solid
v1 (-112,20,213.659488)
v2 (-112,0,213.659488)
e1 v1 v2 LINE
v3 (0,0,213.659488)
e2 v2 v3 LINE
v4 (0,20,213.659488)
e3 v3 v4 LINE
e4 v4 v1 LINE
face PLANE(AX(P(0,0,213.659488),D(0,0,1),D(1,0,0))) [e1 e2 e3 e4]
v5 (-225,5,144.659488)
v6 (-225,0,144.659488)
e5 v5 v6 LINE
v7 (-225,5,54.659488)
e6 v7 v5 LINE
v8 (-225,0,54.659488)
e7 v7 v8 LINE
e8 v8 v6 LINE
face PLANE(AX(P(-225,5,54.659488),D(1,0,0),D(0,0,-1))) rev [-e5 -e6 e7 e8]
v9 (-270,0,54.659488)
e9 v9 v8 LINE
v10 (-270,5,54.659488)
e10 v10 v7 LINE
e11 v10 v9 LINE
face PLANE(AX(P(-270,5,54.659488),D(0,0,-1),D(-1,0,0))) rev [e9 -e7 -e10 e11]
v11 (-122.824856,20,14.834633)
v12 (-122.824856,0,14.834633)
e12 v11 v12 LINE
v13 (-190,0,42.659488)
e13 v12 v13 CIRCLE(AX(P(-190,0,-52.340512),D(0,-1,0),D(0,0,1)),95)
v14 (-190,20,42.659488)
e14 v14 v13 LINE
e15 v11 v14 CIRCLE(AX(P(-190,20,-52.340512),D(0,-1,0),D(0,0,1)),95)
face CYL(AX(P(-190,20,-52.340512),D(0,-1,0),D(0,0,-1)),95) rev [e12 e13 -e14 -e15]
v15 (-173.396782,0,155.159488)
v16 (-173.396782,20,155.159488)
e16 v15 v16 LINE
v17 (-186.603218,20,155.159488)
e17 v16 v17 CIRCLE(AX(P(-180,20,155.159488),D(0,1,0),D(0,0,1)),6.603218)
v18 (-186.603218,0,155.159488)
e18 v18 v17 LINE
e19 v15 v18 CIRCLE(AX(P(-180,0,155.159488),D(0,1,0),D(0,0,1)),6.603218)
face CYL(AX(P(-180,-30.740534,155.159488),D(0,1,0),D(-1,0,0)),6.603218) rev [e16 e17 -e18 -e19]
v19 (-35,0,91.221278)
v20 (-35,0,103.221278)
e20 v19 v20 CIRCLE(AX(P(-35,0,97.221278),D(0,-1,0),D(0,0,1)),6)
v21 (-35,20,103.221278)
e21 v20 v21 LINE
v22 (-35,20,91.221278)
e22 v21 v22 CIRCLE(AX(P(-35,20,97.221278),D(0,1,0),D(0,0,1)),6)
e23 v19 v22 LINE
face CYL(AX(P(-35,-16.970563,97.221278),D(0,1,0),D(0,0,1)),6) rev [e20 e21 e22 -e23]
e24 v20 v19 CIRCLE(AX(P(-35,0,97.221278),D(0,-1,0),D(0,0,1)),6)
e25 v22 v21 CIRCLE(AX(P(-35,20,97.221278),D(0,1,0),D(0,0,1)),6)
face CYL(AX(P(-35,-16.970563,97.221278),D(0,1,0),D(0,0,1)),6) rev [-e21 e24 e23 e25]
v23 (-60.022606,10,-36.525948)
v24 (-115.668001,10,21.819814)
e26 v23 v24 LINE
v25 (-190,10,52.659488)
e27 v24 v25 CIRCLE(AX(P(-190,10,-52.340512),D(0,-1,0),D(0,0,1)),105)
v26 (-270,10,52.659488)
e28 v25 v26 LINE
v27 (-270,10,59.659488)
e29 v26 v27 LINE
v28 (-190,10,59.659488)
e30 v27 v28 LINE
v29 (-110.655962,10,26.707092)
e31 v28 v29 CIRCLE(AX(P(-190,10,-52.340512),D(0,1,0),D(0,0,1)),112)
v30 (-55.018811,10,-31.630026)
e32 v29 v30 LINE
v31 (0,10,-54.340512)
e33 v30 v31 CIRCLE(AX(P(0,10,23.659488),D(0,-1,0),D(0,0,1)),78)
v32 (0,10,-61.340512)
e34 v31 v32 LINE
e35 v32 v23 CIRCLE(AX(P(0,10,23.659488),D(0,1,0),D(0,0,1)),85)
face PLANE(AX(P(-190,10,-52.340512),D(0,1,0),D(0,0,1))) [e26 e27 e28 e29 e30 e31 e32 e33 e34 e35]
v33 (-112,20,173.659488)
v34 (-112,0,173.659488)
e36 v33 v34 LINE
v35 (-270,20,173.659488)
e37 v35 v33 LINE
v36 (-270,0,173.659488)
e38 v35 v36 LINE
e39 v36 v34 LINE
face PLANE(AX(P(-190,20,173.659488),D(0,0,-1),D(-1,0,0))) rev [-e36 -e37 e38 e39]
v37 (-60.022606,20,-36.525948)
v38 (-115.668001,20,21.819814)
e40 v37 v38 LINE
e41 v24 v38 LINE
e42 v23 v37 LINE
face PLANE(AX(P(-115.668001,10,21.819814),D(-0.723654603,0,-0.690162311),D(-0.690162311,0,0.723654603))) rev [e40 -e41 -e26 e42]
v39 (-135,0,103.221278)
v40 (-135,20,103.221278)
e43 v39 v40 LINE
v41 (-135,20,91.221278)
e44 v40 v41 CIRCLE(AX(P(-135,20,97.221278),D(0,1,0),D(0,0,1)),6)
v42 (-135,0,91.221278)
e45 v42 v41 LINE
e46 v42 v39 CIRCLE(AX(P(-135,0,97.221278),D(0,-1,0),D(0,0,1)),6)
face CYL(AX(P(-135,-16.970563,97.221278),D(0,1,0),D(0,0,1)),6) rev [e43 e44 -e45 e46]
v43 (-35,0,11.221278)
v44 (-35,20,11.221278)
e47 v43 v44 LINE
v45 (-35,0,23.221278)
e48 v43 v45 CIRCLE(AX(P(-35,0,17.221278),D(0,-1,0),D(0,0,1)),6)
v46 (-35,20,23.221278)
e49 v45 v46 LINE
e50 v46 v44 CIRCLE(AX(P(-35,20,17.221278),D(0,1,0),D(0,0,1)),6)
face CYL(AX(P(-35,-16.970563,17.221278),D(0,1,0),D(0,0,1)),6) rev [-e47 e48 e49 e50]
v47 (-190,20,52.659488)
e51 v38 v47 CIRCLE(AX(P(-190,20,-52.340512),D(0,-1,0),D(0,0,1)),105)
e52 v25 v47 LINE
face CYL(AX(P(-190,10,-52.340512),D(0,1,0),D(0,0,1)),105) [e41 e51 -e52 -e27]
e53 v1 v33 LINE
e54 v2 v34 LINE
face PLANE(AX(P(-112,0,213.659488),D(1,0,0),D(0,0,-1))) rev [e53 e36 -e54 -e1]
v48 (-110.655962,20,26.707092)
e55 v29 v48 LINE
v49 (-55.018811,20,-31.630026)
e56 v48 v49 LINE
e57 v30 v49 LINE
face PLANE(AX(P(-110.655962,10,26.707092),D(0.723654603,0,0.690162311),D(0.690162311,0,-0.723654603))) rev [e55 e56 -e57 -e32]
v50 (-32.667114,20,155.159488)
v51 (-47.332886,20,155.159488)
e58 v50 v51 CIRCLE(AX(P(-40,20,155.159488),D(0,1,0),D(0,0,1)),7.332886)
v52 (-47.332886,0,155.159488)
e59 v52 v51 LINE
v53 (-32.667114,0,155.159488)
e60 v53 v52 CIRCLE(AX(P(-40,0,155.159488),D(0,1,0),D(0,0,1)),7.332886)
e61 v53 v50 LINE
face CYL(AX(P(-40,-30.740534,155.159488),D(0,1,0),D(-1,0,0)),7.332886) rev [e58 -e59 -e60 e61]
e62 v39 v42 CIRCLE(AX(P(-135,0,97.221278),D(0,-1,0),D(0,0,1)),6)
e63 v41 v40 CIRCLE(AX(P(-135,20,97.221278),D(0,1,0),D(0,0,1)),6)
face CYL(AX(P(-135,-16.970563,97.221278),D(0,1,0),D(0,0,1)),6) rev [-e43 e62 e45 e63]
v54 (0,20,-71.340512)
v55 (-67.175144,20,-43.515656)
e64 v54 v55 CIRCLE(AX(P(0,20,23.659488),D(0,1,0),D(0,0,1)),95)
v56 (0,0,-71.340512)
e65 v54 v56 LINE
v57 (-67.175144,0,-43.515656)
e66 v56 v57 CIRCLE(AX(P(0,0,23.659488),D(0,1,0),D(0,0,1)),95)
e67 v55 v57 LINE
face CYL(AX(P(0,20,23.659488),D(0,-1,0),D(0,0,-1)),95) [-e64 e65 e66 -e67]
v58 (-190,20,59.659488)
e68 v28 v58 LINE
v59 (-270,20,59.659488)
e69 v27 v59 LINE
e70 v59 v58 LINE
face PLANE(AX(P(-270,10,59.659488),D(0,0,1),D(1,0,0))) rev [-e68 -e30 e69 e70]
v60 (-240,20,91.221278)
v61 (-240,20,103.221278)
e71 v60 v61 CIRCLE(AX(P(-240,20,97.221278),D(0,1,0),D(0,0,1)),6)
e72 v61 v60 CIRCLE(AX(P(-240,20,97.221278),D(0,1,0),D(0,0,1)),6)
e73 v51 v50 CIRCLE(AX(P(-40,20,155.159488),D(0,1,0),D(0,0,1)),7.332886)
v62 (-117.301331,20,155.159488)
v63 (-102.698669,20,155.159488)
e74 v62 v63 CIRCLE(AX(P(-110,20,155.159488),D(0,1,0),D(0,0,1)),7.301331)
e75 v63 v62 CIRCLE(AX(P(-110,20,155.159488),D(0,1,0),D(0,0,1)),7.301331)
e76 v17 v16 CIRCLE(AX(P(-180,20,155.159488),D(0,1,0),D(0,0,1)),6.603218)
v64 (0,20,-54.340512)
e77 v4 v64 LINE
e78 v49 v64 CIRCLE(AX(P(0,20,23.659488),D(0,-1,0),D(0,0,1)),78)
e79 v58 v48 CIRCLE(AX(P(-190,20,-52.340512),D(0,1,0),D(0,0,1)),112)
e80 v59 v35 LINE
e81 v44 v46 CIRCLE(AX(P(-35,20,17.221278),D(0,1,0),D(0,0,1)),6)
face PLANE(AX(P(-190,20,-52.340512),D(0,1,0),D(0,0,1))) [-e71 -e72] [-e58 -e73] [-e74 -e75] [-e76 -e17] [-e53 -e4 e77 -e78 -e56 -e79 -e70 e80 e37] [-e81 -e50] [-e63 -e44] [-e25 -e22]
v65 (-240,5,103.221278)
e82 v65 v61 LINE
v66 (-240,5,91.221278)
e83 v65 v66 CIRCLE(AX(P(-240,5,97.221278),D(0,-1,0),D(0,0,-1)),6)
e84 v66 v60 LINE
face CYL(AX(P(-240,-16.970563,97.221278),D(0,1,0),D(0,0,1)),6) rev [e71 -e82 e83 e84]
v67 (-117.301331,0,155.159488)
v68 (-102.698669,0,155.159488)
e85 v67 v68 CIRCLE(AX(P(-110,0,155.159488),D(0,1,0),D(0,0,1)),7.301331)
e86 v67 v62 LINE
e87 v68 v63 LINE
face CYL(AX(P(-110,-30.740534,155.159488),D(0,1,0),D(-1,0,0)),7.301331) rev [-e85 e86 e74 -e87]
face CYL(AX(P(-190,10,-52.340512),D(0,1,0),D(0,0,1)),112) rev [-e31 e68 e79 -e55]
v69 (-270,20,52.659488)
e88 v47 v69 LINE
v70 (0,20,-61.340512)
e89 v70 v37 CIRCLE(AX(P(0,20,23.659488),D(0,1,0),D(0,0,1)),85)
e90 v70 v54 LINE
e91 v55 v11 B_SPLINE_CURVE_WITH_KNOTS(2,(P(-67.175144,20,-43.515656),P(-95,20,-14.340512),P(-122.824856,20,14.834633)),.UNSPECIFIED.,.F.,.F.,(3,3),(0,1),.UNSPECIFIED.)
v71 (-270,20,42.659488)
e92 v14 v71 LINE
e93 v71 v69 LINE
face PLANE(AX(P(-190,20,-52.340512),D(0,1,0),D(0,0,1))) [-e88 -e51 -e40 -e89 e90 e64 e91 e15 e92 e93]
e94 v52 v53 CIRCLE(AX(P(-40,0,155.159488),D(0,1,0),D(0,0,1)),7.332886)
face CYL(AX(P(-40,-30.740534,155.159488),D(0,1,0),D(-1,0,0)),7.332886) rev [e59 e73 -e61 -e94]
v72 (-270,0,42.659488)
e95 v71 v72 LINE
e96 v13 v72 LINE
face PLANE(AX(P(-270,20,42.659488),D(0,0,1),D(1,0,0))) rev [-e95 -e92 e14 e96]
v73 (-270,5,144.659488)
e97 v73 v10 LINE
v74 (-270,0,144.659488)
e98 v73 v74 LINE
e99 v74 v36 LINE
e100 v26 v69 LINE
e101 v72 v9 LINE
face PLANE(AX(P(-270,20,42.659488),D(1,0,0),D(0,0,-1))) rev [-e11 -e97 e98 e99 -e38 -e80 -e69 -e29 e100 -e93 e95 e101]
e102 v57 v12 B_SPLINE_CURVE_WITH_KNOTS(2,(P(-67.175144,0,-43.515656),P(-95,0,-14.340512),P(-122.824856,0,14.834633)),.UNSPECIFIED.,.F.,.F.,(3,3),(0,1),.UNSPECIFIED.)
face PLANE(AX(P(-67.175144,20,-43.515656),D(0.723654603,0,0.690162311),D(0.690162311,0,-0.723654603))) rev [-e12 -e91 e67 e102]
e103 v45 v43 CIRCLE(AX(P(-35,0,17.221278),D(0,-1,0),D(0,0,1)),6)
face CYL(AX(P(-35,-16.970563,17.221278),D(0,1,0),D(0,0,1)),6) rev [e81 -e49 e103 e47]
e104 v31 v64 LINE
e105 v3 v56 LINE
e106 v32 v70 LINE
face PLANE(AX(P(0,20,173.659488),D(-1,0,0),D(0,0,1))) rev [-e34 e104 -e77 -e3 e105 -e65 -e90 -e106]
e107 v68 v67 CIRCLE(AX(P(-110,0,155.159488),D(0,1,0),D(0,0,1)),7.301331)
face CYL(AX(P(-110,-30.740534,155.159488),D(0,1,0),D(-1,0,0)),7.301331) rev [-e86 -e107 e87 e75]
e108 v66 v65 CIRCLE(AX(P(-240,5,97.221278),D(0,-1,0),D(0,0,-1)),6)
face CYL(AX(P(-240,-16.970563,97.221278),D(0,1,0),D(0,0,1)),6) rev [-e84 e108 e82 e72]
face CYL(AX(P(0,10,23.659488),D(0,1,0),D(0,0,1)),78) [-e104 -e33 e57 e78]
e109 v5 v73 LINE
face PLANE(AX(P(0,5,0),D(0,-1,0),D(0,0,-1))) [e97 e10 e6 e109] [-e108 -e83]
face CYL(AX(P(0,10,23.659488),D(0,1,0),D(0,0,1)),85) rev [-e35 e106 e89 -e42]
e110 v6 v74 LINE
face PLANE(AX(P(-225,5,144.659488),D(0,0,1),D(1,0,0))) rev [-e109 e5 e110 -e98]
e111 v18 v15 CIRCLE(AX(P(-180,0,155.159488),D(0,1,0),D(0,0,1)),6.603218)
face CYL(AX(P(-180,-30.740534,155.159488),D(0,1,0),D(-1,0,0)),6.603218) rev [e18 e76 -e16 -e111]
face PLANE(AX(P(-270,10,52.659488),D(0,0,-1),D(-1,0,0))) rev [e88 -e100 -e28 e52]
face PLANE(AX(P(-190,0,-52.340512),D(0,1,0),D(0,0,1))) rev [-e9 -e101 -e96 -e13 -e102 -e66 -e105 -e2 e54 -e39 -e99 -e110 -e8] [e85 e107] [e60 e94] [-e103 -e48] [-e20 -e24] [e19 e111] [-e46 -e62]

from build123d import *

# Parameters (mm, degrees)
EXTRUDE_1_DEPTH      = 20
CUT_EXTRUDE_1_DEPTH  = 10
SKETCH_4_W           = 45
SKETCH_4_H           = 90
CUT_EXTRUDE_2_DEPTH  = 5
SKETCH_5_W           = 112
SKETCH_5_H           = 20
EXTRUDE_2_DEPTH      = 40
CUT_EXTRUDE_3_REACH  = 1227.871
SKETCH_6_R           = 6
SKETCH_6_R_2         = 5
CUT_EXTRUDE_4_REACH  = 1228.116
SKETCH_7_R           = 7.332886018
SKETCH_7_R_2         = 7.301331484
SKETCH_7_R_3         = 6.603217824
SKETCH_24_R          = 6
CUT_EXTRUDE_21_DEPTH = 25


with BuildPart() as part:
    # 草图1 → 凸台-拉伸1 (new body)
    with BuildSketch(Plane(origin=(0, 0, 0), x_dir=(1, 0, 0), z_dir=(0, 1, 0))):
        with BuildLine():
            Line((-190, -173.659488393), (0, -173.659488393))
            Line((0, -173.659488393), (0, 71.340511607))
            ThreePointArc((0, 71.340511607), (-36.354926075, 64.109067196), (-67.175144213, 43.51565582))
            add(Edge.make_bspline(
                [(-122.824855787, -14.834632605), (-95, 14.340511607), (-67.175144213, 43.51565582)],
                knots=[0, 0, 0, 1, 1, 1], degree=2))
            ThreePointArc((-122.824855787, -14.834632605), (-153.645073925, -35.428043981), (-190, -42.659488393))
            Line((-190, -42.659488393), (-270, -42.659488393))
            Line((-270, -42.659488393), (-270, -173.659488393))
            Line((-270, -173.659488393), (-190, -173.659488393))
        make_face()
    extrude(amount=EXTRUDE_1_DEPTH)

    # 草图2 → 切除-拉伸1 (cut)
    with BuildSketch(Plane(origin=(0, 20, 0), x_dir=(1, 0, 0), z_dir=(0, 1, 0))):
        with BuildLine():
            Line((-270, -52.659488393), (-190, -52.659488393))
            ThreePointArc((-190, -52.659488393), (-149.762170559, -44.64359576), (-115.668000558, -21.819813762))
            Line((-115.668000558, -21.819813762), (-60.022606457, 36.52594767))
            ThreePointArc((-60.022606457, 36.52594767), (-32.474897495, 54.892284551), (0, 61.340511607))
            Line((0, 61.340511607), (0, 54.340511607))
            ThreePointArc((0, 54.340511607), (-29.760862596, 48.439686759), (-55.01881141, 31.630025903))
            Line((-55.01881141, 31.630025903), (-110.655962205, -26.707092192))
            ThreePointArc((-110.655962205, -26.707092192), (-147.042646878, -51.093843482), (-190, -59.659488393))
            Line((-190, -59.659488393), (-270, -59.659488393))
            Line((-270, -59.659488393), (-270, -52.659488393))
        make_face()
    extrude(amount=-CUT_EXTRUDE_1_DEPTH, mode=Mode.SUBTRACT)

    # 草图4 → 切除-拉伸2 (cut)
    with BuildSketch(Plane.XZ):
        with Locations((-247.5, 99.659488393)):
            Rectangle(SKETCH_4_W, SKETCH_4_H)
    extrude(amount=-CUT_EXTRUDE_2_DEPTH, mode=Mode.SUBTRACT)

    # 草图5 → 凸台-拉伸2 (add)
    with BuildSketch(Plane.XY.offset(173.659488393)):
        with Locations((-56, 10)):
            Rectangle(SKETCH_5_W, SKETCH_5_H)
    extrude(amount=EXTRUDE_2_DEPTH)

    # 切除-拉伸3: up to this face of the body (flat: up to its plane)
    cut_extrude_3_end = Plane(part.part.faces().sort_by_distance((-99.039367246, 0, 91.650022184))[0])
    # 草图6 → 切除-拉伸3 (cut, up to the picked face)
    with BuildSketch(Plane(origin=(600.126281628, 25, -649.482989384), x_dir=(0, 0, -1), z_dir=(0, 1, 0)), mode=Mode.PRIVATE) as cut_extrude_3_sk1:
        with Locations(Location((-666.704267343, 635.126281628, 0), (0, 0, 180))):
            Circle(SKETCH_6_R)
    cut_extrude_3_tool1 = split(extrude(cut_extrude_3_sk1.sketch, amount=-CUT_EXTRUDE_3_REACH, mode=Mode.PRIVATE), bisect_by=cut_extrude_3_end, keep=Keep.BOTH, mode=Mode.PRIVATE)
    # 草图6 → 切除-拉伸3 (cut, up to the picked face)
    with BuildSketch(Plane(origin=(600.126281628, 25, -649.482989384), x_dir=(0, 0, -1), z_dir=(0, 1, 0)), mode=Mode.PRIVATE) as cut_extrude_3_sk2:
        with Locations(Location((-746.704267343, 635.126281628, 0), (0, 0, 180))):
            Circle(SKETCH_6_R_2)
    cut_extrude_3_tool2 = split(extrude(cut_extrude_3_sk2.sketch, amount=-CUT_EXTRUDE_3_REACH, mode=Mode.PRIVATE), bisect_by=cut_extrude_3_end, keep=Keep.BOTH, mode=Mode.PRIVATE)
    # 草图6 → 切除-拉伸3 (cut, up to the picked face)
    with BuildSketch(Plane(origin=(600.126281628, 25, -649.482989384), x_dir=(0, 0, -1), z_dir=(0, 1, 0)), mode=Mode.PRIVATE) as cut_extrude_3_sk3:
        with Locations(Location((-746.704267343, 840.126281628, 0), (0, 0, 180))):
            Circle(SKETCH_6_R)
    cut_extrude_3_tool3 = split(extrude(cut_extrude_3_sk3.sketch, amount=-CUT_EXTRUDE_3_REACH, mode=Mode.PRIVATE), bisect_by=cut_extrude_3_end, keep=Keep.BOTH, mode=Mode.PRIVATE)
    # 草图6 → 切除-拉伸3 (cut, up to the picked face)
    with BuildSketch(Plane(origin=(600.126281628, 25, -649.482989384), x_dir=(0, 0, -1), z_dir=(0, 1, 0)), mode=Mode.PRIVATE) as cut_extrude_3_sk4:
        with Locations(Location((-746.704267343, 735.126281628, 0), (0, 0, 180))):
            Circle(SKETCH_6_R)
    cut_extrude_3_tool4 = split(extrude(cut_extrude_3_sk4.sketch, amount=-CUT_EXTRUDE_3_REACH, mode=Mode.PRIVATE), bisect_by=cut_extrude_3_end, keep=Keep.BOTH, mode=Mode.PRIVATE)
    add(cut_extrude_3_tool1.solids().sort_by(Axis((-35, 25, 17.221278), (0, -1, 0)))[0], mode=Mode.SUBTRACT)
    add(cut_extrude_3_tool2.solids().sort_by(Axis((-35, 25, 97.221278), (0, -1, 0)))[0], mode=Mode.SUBTRACT)
    add(cut_extrude_3_tool3.solids().sort_by(Axis((-240, 25, 97.221278), (0, -1, 0)))[0], mode=Mode.SUBTRACT)
    add(cut_extrude_3_tool4.solids().sort_by(Axis((-135, 25, 97.221278), (0, -1, 0)))[0], mode=Mode.SUBTRACT)

    # 草图7 → 切除-拉伸4 (cut, up to next)
    with BuildSketch(Plane(origin=(600.126281628, 35, -649.482989384), x_dir=(0, 0, -1), z_dir=(0, 1, 0)), mode=Mode.PRIVATE) as cut_extrude_4_sk1:
        with Locations(Location((-804.642477777, 640.126281628, 0), (0, 0, 180))):
            Circle(SKETCH_7_R)
    cut_extrude_4_tool1 = extrude(cut_extrude_4_sk1.sketch, amount=-CUT_EXTRUDE_4_REACH, mode=Mode.PRIVATE) & part.part
    # 草图7 → 切除-拉伸4 (cut, up to next)
    with BuildSketch(Plane(origin=(600.126281628, 35, -649.482989384), x_dir=(0, 0, -1), z_dir=(0, 1, 0)), mode=Mode.PRIVATE) as cut_extrude_4_sk2:
        with Locations(Location((-804.642477777, 710.126281628, 0), (0, 0, 180))):
            Circle(SKETCH_7_R_2)
    cut_extrude_4_tool2 = extrude(cut_extrude_4_sk2.sketch, amount=-CUT_EXTRUDE_4_REACH, mode=Mode.PRIVATE) & part.part
    # 草图7 → 切除-拉伸4 (cut, up to next)
    with BuildSketch(Plane(origin=(600.126281628, 35, -649.482989384), x_dir=(0, 0, -1), z_dir=(0, 1, 0)), mode=Mode.PRIVATE) as cut_extrude_4_sk3:
        with Locations(Location((-804.642477777, 780.126281628, 0), (0, 0, 180))):
            Circle(SKETCH_7_R_3)
    cut_extrude_4_tool3 = extrude(cut_extrude_4_sk3.sketch, amount=-CUT_EXTRUDE_4_REACH, mode=Mode.PRIVATE) & part.part
    add(cut_extrude_4_tool1.solids().sort_by_distance((-40, 35, 155.159488))[0], mode=Mode.SUBTRACT)
    add(cut_extrude_4_tool2.solids().sort_by_distance((-110, 35, 155.159488))[0], mode=Mode.SUBTRACT)
    add(cut_extrude_4_tool3.solids().sort_by_distance((-180, 35, 155.159488))[0], mode=Mode.SUBTRACT)

    # 草图24 → 切除-拉伸21 (cut)
    with BuildSketch(Plane(origin=(600.126281628, 25, -649.482989384), x_dir=(0, 0, -1), z_dir=(0, 1, 0))):
        with Locations(Location((-666.704267343, 635.126281628, 0), (0, 0, 180))):
            Circle(SKETCH_24_R)
        with Locations(Location((-746.704267343, 635.126281628, 0), (0, 0, 180))):
            Circle(SKETCH_24_R)
        with Locations(Location((-746.704267343, 840.126281628, 0), (0, 0, 180))):
            Circle(SKETCH_24_R)
        with Locations(Location((-746.704267343, 735.126281628, 0), (0, 0, 180))):
            Circle(SKETCH_24_R)
    extrude(amount=-CUT_EXTRUDE_21_DEPTH, mode=Mode.SUBTRACT)


solid = part.part
